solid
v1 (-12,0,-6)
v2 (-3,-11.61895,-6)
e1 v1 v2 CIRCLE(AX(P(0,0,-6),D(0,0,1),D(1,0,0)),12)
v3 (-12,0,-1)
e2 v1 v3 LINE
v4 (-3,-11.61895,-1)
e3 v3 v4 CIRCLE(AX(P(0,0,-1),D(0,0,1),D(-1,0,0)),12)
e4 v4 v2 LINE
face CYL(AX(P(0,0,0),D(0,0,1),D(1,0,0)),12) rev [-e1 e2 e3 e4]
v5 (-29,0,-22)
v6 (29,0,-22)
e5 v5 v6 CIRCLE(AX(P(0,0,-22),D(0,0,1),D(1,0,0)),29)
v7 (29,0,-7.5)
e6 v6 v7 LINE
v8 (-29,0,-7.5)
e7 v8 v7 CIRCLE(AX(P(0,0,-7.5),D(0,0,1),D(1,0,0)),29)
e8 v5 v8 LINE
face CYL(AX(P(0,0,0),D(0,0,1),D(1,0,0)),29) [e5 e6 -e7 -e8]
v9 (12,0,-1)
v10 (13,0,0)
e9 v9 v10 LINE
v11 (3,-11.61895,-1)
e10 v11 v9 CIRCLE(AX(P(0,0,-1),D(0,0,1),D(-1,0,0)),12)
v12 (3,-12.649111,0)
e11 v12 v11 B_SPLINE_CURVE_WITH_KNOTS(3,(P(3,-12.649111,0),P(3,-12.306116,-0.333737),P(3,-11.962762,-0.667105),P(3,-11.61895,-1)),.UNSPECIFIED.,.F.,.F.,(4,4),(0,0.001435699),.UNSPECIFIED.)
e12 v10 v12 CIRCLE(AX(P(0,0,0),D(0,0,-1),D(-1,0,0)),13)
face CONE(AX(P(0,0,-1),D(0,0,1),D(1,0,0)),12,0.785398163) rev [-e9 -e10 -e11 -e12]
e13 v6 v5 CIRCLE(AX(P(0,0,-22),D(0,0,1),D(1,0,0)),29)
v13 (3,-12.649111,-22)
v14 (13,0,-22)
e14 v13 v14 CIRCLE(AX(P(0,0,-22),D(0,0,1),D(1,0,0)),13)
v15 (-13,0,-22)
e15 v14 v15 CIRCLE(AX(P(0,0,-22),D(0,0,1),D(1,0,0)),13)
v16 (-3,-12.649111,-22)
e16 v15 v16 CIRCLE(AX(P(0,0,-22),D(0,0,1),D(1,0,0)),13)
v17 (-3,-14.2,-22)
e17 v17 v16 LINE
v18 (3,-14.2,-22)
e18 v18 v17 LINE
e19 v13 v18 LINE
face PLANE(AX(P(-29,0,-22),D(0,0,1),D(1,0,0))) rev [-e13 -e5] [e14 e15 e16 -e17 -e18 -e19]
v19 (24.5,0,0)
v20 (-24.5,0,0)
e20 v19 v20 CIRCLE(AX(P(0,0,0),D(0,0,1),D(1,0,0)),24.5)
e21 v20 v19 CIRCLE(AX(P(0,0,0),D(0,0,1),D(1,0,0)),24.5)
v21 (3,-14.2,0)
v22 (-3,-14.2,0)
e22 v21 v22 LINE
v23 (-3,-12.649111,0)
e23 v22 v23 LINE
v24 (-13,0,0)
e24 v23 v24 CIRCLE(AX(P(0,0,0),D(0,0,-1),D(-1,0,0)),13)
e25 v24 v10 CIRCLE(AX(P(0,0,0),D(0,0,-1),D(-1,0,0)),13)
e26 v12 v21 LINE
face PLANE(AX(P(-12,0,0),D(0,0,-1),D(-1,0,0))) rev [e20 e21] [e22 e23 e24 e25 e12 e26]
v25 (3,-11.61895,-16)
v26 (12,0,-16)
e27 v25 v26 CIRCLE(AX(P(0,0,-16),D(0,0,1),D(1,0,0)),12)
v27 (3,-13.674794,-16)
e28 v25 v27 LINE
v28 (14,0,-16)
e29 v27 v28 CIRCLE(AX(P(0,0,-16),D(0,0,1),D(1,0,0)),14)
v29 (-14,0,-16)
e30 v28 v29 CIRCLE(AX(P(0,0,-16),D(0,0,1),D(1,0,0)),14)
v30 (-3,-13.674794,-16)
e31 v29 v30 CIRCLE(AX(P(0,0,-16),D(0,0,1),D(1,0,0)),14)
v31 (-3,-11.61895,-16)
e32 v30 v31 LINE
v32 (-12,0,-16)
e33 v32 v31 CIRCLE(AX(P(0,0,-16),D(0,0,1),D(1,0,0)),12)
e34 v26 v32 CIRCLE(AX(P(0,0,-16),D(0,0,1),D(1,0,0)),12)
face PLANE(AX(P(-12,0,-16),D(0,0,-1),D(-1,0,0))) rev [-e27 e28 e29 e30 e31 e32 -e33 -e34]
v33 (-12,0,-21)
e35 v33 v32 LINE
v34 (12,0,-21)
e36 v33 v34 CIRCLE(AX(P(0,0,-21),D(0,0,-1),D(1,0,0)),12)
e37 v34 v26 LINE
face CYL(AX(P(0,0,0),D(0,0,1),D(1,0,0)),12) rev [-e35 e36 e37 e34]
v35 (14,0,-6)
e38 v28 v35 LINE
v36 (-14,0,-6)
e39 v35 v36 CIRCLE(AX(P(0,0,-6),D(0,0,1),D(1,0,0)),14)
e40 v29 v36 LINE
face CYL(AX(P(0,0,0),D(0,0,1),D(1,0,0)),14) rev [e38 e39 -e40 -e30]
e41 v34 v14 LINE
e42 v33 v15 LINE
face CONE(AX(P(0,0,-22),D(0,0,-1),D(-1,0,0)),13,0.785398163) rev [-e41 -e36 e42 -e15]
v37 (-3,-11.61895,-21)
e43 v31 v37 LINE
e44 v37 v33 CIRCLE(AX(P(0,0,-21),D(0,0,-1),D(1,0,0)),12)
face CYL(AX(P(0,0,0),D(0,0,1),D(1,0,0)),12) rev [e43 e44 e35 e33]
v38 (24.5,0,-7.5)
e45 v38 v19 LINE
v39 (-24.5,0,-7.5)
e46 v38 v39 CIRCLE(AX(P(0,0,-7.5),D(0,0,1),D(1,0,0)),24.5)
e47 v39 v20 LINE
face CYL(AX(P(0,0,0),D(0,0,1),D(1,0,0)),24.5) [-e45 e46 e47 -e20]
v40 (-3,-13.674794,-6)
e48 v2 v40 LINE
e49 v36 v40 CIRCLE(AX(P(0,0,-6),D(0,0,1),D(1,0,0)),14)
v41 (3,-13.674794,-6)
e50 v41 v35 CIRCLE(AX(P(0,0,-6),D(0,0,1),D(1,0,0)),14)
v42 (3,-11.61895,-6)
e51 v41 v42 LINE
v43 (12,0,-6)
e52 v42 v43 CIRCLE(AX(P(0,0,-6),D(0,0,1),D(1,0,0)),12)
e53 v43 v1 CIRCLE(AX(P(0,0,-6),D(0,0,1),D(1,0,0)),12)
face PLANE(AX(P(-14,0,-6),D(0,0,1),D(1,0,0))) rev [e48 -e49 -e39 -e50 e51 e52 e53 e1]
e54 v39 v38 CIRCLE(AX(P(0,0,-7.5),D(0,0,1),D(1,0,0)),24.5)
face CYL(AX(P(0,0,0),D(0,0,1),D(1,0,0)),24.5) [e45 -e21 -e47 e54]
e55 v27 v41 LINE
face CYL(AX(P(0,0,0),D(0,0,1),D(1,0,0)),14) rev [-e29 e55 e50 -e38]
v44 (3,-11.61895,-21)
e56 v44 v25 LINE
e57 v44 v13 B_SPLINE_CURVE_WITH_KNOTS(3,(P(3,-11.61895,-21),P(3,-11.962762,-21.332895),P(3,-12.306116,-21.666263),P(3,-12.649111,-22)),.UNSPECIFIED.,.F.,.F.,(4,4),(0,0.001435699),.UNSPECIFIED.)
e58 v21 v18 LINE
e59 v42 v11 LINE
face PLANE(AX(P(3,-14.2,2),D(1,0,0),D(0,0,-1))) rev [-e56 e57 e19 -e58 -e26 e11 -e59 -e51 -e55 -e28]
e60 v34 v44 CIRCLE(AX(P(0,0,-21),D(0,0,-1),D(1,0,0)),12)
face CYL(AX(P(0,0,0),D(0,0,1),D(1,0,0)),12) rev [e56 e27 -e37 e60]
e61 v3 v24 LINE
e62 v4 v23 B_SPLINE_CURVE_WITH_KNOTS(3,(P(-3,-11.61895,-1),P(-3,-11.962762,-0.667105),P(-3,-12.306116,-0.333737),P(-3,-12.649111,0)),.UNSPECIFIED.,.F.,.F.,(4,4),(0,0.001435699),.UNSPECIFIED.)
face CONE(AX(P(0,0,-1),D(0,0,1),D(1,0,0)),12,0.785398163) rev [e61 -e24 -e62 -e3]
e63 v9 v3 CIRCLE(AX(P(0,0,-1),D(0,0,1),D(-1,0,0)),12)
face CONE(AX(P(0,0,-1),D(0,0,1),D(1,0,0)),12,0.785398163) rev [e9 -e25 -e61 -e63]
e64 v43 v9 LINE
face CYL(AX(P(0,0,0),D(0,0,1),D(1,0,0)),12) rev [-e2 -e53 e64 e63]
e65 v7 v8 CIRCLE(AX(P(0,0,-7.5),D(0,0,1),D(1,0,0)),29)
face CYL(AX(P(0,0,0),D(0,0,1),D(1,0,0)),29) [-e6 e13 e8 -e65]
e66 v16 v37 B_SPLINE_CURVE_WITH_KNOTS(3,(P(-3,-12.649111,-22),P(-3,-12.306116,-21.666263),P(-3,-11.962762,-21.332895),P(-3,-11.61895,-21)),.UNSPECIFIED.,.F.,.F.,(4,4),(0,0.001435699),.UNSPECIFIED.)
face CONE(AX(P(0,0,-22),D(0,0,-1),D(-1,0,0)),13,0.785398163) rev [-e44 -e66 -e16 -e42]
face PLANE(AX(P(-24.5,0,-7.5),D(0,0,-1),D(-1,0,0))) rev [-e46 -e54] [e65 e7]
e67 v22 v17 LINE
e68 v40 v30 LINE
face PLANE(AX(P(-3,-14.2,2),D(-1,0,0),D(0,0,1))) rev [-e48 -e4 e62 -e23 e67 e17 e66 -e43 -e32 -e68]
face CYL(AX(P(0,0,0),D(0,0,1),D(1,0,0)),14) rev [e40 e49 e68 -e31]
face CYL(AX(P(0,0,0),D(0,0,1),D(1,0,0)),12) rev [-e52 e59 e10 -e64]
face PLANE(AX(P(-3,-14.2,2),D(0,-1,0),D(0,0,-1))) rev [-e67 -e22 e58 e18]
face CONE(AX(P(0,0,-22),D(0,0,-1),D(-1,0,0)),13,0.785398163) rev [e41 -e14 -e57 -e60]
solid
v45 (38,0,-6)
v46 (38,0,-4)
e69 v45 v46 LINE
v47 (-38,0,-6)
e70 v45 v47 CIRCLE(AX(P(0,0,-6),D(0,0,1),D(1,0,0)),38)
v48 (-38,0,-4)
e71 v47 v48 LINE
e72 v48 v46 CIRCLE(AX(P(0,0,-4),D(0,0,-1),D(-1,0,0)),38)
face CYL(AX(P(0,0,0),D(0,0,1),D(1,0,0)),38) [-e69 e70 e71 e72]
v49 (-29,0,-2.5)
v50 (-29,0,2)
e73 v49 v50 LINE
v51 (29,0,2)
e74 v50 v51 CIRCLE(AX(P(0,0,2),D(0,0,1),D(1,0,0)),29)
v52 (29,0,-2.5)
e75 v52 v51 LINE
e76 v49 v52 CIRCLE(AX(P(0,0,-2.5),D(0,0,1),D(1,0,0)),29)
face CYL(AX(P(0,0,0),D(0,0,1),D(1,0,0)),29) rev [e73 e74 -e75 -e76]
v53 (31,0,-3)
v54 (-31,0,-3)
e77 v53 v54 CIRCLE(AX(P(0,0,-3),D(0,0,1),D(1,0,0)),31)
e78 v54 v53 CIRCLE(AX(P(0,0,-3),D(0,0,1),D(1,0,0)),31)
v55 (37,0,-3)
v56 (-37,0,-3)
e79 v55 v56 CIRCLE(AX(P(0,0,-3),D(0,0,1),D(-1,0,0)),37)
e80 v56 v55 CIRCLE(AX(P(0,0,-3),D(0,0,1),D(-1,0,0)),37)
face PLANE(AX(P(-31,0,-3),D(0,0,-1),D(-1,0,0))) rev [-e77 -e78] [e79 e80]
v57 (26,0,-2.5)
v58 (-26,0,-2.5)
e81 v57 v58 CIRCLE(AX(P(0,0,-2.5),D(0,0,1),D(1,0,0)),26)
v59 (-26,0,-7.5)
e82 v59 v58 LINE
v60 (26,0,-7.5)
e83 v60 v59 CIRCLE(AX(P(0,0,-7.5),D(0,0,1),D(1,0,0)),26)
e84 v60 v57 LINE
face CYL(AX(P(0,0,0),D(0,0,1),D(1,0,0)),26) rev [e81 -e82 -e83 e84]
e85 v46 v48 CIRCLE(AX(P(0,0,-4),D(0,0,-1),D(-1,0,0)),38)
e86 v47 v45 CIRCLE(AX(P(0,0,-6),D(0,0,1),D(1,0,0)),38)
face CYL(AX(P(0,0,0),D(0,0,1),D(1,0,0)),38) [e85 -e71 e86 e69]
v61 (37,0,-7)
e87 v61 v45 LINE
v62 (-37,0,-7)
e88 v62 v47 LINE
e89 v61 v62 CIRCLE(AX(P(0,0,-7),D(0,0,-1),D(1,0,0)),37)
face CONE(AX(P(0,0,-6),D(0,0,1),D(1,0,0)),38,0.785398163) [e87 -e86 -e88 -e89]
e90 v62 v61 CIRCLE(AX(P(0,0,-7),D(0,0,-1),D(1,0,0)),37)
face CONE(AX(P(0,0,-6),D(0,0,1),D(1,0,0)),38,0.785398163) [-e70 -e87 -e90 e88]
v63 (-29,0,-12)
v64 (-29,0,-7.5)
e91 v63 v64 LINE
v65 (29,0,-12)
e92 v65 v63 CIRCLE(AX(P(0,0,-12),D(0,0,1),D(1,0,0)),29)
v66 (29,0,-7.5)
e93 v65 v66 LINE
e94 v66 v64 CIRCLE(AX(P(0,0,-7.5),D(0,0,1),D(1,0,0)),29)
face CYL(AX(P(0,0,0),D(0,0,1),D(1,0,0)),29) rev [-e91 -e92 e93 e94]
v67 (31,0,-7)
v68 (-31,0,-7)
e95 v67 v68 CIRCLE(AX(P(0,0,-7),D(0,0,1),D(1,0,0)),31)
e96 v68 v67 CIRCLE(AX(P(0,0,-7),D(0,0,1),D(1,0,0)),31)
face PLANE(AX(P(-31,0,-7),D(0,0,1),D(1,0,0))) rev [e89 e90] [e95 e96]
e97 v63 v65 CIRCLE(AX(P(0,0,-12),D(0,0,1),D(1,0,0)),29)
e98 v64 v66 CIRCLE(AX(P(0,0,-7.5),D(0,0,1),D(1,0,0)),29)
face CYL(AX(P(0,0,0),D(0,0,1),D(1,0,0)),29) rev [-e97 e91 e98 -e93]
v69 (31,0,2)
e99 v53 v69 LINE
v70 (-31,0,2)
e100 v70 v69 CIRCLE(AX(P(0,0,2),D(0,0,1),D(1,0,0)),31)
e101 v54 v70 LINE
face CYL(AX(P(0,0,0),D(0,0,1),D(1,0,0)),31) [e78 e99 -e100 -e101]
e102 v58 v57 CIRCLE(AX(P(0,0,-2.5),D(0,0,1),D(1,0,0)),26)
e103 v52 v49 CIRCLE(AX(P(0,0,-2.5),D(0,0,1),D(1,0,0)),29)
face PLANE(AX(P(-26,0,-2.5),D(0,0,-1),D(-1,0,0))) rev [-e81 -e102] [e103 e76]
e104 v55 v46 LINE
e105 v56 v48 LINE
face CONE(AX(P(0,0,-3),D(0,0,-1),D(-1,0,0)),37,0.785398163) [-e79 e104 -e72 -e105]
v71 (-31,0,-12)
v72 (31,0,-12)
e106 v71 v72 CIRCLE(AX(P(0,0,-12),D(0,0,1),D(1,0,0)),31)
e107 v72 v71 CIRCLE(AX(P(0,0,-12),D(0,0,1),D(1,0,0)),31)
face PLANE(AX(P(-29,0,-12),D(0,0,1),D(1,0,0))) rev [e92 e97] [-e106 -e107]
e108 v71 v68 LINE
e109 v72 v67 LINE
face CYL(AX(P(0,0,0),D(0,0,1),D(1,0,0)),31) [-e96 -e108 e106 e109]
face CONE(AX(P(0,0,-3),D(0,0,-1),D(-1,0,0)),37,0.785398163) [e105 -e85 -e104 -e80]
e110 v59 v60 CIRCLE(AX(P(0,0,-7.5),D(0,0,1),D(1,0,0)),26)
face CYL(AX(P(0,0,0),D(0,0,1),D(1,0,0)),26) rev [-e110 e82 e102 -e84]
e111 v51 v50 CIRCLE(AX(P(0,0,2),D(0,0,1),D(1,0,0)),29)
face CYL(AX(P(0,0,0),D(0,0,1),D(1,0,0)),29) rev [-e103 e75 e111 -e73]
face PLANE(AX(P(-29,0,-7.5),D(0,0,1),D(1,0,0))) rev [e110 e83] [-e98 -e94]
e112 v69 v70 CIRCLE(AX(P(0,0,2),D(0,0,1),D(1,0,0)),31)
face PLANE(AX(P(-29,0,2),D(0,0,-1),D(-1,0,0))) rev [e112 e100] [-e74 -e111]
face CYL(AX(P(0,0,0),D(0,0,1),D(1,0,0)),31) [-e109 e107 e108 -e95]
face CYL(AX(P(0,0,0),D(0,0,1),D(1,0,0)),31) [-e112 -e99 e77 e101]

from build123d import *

# Parameters (mm, degrees)
CHAMFER_1_SIZE      = 1
SKETCH_3_W          = 6
SKETCH_3_H          = 4.4
CUT_EXTRUDE_1_DEPTH = 59.855755878
CHAMFER_2_SIZE      = 1


with BuildPart() as part:
    # 草图1 → 旋转1 (revolve)
    with BuildSketch(Plane(origin=(0, 0, 0), x_dir=(1, 0, 0), z_dir=(0, 1, 0)), mode=Mode.PRIVATE) as revolve_1_sk:
        Polygon((-12, 22), (-12, 16), (-14, 16), (-14, 6), (-12, 6), (-12, 0), (-24.5, 0), (-24.5, 7.5), (-29, 7.5), (-29, 22), align=None)
    revolve(revolve_1_sk.sketch.rotate(Axis((0, 0, 0), (0, 0, -1)), 180), axis=Axis((0, 0, 0), (0, 0, -1)))

    # 草图3 → 切除-拉伸1 (cut, through all)
    with BuildSketch(Plane(origin=(0, 0, -22), x_dir=(-1, 0, 0), z_dir=(0, 0, -1))):
        with Locations((0, -12)):
            Rectangle(SKETCH_3_W, SKETCH_3_H)
    extrude(amount=-CUT_EXTRUDE_1_DEPTH, mode=Mode.SUBTRACT)

    # 倒角2
    chamfer_2_edges = [part.edges().sort_by_distance(p)[0] for p in [
        (0, 12, 0),
        (0, 12, -22),
    ]]
    chamfer(chamfer_2_edges, length=CHAMFER_2_SIZE)


with BuildPart() as body_2:
    # 草图2 → 旋转2 (revolve)
    with BuildSketch(Plane(origin=(0, 0, 0), x_dir=(1, 0, 0), z_dir=(0, 1, 0)), mode=Mode.PRIVATE) as revolve_2_sk:
        Polygon((-29, 12), (-29, 7.5), (-26, 7.5), (-26, 2.5), (-29, 2.5), (-29, -2), (-31, -2), (-31, 3), (-38, 3), (-38, 7), (-31, 7), (-31, 12), align=None)
    revolve(revolve_2_sk.sketch.rotate(Axis((0, 0, 0), (0, 0, -1)), 180), axis=Axis((0, 0, 0), (0, 0, -1)))

    # 倒角1
    chamfer_1_edges = [body_2.edges().sort_by_distance(p)[0] for p in [
        (-38, 0, -7),
        (-38, 0, -3),
    ]]
    chamfer(chamfer_1_edges, length=CHAMFER_1_SIZE)


solid = Compound([part.part, body_2.part])
